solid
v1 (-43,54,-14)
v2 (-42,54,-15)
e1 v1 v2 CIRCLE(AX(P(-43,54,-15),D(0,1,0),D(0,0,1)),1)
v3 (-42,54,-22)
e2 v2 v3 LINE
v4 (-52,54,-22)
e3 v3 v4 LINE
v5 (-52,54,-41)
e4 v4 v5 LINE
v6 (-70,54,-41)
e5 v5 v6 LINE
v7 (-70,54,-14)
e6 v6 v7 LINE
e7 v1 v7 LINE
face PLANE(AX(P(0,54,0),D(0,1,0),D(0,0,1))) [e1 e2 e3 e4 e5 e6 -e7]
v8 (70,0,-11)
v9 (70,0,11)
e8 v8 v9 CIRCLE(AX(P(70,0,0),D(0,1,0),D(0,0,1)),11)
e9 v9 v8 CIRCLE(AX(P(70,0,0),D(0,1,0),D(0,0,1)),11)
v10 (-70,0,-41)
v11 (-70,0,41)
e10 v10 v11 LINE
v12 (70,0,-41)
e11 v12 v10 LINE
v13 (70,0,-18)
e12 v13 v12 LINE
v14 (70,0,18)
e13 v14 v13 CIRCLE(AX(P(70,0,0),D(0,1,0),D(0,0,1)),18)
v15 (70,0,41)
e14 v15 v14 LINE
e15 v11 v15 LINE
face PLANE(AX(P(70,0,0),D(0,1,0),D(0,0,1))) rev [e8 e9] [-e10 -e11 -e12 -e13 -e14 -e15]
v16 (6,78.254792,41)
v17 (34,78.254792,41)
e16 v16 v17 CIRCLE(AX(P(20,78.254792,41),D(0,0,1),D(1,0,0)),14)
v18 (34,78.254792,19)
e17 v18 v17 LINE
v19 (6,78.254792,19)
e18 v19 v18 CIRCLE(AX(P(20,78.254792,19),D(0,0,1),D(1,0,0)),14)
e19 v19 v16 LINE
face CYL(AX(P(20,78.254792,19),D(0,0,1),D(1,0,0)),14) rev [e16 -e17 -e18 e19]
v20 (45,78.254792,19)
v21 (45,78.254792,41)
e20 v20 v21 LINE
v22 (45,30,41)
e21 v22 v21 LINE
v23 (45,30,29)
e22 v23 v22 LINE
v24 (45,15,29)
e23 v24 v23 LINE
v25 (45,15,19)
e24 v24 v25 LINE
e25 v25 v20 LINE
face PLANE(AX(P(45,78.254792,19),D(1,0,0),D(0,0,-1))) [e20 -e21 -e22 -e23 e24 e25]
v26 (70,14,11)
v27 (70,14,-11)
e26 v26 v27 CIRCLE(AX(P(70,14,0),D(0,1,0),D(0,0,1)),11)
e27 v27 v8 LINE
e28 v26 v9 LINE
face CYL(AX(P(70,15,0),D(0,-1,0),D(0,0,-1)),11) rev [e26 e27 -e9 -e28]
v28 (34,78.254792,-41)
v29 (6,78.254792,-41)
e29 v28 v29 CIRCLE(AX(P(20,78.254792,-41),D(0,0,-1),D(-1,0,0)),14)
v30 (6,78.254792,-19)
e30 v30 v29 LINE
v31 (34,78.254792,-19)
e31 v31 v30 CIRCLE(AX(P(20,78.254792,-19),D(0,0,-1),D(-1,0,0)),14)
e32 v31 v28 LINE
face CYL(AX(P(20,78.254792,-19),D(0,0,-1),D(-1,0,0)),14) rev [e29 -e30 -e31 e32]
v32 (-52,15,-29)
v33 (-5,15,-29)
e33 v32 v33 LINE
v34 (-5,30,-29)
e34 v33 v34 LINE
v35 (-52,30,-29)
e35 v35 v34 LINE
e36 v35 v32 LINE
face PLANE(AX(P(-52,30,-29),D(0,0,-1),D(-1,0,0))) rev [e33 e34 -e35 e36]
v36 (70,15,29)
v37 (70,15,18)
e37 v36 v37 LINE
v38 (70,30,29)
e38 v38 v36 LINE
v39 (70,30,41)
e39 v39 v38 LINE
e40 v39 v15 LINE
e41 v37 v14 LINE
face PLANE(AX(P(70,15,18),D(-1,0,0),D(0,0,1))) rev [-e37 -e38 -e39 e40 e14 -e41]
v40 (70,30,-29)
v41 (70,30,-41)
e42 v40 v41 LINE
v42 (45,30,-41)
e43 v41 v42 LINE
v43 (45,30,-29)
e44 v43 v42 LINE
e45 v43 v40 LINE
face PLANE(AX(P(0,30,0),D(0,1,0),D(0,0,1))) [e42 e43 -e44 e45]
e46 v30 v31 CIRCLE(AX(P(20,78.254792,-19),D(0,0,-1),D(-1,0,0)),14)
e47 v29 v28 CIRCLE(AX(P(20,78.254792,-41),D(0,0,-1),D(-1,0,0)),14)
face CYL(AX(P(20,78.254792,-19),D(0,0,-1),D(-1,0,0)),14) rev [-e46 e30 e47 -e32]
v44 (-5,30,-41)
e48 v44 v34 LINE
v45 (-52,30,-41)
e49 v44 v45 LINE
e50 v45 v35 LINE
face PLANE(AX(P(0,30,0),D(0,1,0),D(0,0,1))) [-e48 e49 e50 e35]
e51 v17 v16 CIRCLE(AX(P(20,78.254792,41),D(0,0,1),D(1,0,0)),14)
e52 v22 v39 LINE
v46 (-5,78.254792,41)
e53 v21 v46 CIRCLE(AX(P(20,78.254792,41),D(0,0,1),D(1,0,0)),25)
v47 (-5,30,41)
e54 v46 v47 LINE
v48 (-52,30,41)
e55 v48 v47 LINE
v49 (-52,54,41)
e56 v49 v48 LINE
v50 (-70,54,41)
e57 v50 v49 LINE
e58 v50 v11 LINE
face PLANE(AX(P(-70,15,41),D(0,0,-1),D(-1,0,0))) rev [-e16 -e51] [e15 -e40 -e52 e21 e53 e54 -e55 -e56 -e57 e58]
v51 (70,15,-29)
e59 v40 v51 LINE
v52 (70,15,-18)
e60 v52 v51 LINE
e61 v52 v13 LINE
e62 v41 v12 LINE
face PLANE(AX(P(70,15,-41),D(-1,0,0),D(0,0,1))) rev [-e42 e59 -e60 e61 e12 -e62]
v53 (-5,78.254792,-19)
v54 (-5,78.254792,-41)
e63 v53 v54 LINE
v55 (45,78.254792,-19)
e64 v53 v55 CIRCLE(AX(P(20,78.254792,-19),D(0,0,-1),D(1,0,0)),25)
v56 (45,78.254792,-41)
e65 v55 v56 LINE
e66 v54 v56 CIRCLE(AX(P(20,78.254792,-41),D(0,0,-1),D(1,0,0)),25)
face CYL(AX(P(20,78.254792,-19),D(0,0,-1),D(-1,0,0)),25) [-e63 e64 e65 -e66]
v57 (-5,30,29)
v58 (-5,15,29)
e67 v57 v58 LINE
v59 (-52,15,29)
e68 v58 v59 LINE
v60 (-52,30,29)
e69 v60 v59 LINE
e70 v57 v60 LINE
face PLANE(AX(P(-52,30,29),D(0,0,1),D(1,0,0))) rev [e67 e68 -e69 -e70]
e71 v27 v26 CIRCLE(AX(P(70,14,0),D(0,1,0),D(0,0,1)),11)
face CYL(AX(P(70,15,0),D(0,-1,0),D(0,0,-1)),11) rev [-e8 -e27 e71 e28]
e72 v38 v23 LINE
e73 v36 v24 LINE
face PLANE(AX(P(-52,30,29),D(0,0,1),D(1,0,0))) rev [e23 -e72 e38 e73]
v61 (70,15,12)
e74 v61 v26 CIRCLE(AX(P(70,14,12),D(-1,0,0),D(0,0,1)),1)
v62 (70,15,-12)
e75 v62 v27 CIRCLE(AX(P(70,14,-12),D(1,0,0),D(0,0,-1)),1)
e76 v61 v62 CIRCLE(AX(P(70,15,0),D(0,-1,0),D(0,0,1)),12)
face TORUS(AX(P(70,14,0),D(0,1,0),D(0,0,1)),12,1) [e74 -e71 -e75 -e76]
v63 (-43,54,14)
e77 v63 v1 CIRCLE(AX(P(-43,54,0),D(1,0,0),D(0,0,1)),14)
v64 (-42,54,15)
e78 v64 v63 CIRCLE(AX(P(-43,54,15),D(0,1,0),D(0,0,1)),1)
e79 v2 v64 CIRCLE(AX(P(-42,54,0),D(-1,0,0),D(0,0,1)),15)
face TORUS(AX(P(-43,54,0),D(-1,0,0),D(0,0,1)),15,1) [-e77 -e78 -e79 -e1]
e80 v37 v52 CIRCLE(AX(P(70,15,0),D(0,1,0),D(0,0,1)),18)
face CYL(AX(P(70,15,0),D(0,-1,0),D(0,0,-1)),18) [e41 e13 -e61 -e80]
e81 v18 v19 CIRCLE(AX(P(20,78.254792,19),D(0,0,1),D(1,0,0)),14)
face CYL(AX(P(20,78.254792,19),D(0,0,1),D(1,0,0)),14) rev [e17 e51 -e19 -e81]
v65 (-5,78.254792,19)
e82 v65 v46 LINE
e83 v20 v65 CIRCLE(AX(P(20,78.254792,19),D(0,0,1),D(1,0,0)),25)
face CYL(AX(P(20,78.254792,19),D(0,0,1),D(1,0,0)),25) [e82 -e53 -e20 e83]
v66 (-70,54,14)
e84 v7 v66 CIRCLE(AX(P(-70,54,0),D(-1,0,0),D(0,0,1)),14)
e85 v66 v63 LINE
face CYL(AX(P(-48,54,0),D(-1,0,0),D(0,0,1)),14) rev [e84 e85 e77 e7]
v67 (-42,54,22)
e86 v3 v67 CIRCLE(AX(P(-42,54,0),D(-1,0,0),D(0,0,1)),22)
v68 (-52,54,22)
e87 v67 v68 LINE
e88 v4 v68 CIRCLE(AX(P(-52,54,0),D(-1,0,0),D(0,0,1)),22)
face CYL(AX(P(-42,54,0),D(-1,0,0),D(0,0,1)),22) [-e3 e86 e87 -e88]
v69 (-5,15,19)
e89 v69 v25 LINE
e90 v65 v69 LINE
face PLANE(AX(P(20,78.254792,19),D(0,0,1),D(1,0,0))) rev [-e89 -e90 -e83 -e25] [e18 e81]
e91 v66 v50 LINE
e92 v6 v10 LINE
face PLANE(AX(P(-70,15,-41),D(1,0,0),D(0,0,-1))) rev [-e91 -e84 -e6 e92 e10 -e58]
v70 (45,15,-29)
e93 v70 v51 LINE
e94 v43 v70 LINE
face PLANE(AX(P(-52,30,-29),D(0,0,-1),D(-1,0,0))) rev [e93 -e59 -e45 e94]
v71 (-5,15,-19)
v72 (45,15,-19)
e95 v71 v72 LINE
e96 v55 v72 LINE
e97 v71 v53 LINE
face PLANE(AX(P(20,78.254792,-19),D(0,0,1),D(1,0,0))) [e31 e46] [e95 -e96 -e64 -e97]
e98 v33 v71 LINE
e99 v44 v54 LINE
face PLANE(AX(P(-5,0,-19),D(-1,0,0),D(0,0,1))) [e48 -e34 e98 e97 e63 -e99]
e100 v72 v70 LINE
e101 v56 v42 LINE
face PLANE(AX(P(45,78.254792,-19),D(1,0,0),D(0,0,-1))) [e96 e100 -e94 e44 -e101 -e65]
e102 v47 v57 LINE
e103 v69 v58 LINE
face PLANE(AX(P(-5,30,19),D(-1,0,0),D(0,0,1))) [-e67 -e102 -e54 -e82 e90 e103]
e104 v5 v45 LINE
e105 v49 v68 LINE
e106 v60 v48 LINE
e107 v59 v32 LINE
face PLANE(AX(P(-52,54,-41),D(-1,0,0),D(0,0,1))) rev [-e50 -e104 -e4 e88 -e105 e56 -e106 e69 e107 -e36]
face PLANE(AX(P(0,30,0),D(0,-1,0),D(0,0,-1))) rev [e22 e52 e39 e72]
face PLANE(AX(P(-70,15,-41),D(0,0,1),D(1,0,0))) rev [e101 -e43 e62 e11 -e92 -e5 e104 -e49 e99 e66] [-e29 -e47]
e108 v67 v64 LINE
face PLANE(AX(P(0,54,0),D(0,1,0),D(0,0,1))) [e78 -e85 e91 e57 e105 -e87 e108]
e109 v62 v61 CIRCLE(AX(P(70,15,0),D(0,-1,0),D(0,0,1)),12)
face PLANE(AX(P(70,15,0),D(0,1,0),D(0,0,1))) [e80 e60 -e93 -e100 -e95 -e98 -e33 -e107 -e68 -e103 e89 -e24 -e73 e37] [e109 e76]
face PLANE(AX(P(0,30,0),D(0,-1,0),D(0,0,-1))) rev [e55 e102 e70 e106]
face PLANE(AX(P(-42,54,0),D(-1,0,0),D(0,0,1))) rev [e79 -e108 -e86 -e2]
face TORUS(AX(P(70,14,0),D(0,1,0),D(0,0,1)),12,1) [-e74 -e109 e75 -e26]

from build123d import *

# Parameters (mm, degrees)
BASE_PLATE_SKETCH_R     = 11
BASE_PLATE_DEPTH        = 15
REAR_WALL_SKETCH_W      = 18
REAR_WALL_SKETCH_H      = 82
REAR_WALL_DEPTH         = 39
STEP_BLOCKS_SKETCH_W    = 122
STEP_BLOCKS_SKETCH_H    = 12
STEP_BLOCKS_DEPTH       = 15
BEARING_EAR_1_SKETCH_R  = 14
BEARING_EAR_1_DEPTH     = 22
BEARING_START           = -22
BEARING_EAR_2_SKETCH_R  = 14
BEARING_EAR_2_DEPTH     = 22
SADDLE_CUT_DEPTH        = 22
SADDLE_BOSS_DEPTH       = 28
SADDLE_BOSS_FILLET_R1_R = 1
BASE_EDGE_FILLET_R1_R   = 1


with BuildPart() as part:
    # Base Plate Sketch → Base Plate (new body)
    with BuildSketch(Plane(origin=(0, 0, 0), x_dir=(1, 0, 0), z_dir=(0, 1, 0))):
        with BuildLine():
            Line((70, -18), (70, -41))
            Line((70, -41), (-70, -41))
            Line((-70, -41), (-70, 41))
            Line((-70, 41), (70, 41))
            Line((70, 41), (70, 18))
            ThreePointArc((70, 18), (88, 0), (70, -18))
        make_face()
        with Locations(Location((70, 0, 0), (0, 0, 270))):
            Circle(BASE_PLATE_SKETCH_R, mode=Mode.SUBTRACT)
    extrude(amount=BASE_PLATE_DEPTH)

    # Rear Wall Sketch → Rear Wall (add)
    with BuildSketch(Plane(origin=(0, 15, 0), x_dir=(1, 0, 0), z_dir=(0, 1, 0))):
        with Locations((-61, 0)):
            Rectangle(REAR_WALL_SKETCH_W, REAR_WALL_SKETCH_H)
    extrude(amount=REAR_WALL_DEPTH)

    # Step Blocks Sketch → Step Blocks (add)
    with BuildSketch(Plane(origin=(0, 15, 0), x_dir=(1, 0, 0), z_dir=(0, 1, 0))):
        with Locations((9, 35)):
            Rectangle(STEP_BLOCKS_SKETCH_W, STEP_BLOCKS_SKETCH_H)
        with Locations((9, -35)):
            Rectangle(STEP_BLOCKS_SKETCH_W, STEP_BLOCKS_SKETCH_H)
    extrude(amount=STEP_BLOCKS_DEPTH)

    # Bearing Ear 1 Sketch → Bearing Ear 1 (add)
    with BuildSketch(Plane.XY.offset(41)):
        with BuildLine():
            Line((-5, 78.254792273), (-5, 30))
            Line((-5, 30), (-5, 0))
            Line((-5, 0), (45, 0))
            Line((45, 0), (45, 30))
            Line((45, 30), (45, 78.254792273))
            ThreePointArc((45, 78.254792273), (20, 103.254792273), (-5, 78.254792273))
        make_face()
        with Locations((20, 78.254792273)):
            Circle(BEARING_EAR_1_SKETCH_R, mode=Mode.SUBTRACT)
    extrude(amount=-BEARING_EAR_1_DEPTH)

    # Bearing Ear 2 Sketch → Bearing Ear 2 (add)
    with BuildSketch(Plane(origin=(0, 0, -41), x_dir=(-1, 0, 0), z_dir=(0, 0, -1)).offset(BEARING_START)):
        with BuildLine():
            Line((-45, 78.254792273), (-45, 0))
            Line((-45, 0), (5, 0))
            Line((5, 0), (5, 78.254792273))
            ThreePointArc((5, 78.254792273), (-20, 103.254792273), (-45, 78.254792273))
        make_face()
        with Locations(Location((-20, 78.254792273, 0), (0, 0, 180))):
            Circle(BEARING_EAR_2_SKETCH_R, mode=Mode.SUBTRACT)
    extrude(amount=BEARING_EAR_2_DEPTH)

    # Saddle Cut Sketch → Saddle Cut (cut)
    with BuildSketch(Plane.ZY.offset(70)):
        with BuildLine():
            Line((-14, 54), (14, 54))
            ThreePointArc((14, 54), (0, 40), (-14, 54))
        make_face()
    extrude(amount=-SADDLE_CUT_DEPTH, mode=Mode.SUBTRACT)

    # Saddle Boss Sketch → Saddle Boss (add)
    with BuildSketch(Plane.ZY.offset(70)):
        with BuildLine():
            Line((-14, 54), (-22, 54))
            ThreePointArc((-22, 54), (0, 32), (22, 54))
            Line((22, 54), (14, 54))
            ThreePointArc((14, 54), (0, 40), (-14, 54))
        make_face()
    extrude(amount=-SADDLE_BOSS_DEPTH)

    # Saddle Boss Fillet R1
    saddle_boss_fillet_r1_edges = [part.edges().sort_by_distance(p)[0] for p in [
        (-42, 40, 0),
    ]]
    fillet(saddle_boss_fillet_r1_edges, radius=SADDLE_BOSS_FILLET_R1_R)

    # Base Edge Fillet R1
    base_edge_fillet_r1_edges = [part.edges().sort_by_distance(p)[0] for p in [
        (70, 15, -11),
    ]]
    fillet(base_edge_fillet_r1_edges, radius=BASE_EDGE_FILLET_R1_R)


solid = part.part
